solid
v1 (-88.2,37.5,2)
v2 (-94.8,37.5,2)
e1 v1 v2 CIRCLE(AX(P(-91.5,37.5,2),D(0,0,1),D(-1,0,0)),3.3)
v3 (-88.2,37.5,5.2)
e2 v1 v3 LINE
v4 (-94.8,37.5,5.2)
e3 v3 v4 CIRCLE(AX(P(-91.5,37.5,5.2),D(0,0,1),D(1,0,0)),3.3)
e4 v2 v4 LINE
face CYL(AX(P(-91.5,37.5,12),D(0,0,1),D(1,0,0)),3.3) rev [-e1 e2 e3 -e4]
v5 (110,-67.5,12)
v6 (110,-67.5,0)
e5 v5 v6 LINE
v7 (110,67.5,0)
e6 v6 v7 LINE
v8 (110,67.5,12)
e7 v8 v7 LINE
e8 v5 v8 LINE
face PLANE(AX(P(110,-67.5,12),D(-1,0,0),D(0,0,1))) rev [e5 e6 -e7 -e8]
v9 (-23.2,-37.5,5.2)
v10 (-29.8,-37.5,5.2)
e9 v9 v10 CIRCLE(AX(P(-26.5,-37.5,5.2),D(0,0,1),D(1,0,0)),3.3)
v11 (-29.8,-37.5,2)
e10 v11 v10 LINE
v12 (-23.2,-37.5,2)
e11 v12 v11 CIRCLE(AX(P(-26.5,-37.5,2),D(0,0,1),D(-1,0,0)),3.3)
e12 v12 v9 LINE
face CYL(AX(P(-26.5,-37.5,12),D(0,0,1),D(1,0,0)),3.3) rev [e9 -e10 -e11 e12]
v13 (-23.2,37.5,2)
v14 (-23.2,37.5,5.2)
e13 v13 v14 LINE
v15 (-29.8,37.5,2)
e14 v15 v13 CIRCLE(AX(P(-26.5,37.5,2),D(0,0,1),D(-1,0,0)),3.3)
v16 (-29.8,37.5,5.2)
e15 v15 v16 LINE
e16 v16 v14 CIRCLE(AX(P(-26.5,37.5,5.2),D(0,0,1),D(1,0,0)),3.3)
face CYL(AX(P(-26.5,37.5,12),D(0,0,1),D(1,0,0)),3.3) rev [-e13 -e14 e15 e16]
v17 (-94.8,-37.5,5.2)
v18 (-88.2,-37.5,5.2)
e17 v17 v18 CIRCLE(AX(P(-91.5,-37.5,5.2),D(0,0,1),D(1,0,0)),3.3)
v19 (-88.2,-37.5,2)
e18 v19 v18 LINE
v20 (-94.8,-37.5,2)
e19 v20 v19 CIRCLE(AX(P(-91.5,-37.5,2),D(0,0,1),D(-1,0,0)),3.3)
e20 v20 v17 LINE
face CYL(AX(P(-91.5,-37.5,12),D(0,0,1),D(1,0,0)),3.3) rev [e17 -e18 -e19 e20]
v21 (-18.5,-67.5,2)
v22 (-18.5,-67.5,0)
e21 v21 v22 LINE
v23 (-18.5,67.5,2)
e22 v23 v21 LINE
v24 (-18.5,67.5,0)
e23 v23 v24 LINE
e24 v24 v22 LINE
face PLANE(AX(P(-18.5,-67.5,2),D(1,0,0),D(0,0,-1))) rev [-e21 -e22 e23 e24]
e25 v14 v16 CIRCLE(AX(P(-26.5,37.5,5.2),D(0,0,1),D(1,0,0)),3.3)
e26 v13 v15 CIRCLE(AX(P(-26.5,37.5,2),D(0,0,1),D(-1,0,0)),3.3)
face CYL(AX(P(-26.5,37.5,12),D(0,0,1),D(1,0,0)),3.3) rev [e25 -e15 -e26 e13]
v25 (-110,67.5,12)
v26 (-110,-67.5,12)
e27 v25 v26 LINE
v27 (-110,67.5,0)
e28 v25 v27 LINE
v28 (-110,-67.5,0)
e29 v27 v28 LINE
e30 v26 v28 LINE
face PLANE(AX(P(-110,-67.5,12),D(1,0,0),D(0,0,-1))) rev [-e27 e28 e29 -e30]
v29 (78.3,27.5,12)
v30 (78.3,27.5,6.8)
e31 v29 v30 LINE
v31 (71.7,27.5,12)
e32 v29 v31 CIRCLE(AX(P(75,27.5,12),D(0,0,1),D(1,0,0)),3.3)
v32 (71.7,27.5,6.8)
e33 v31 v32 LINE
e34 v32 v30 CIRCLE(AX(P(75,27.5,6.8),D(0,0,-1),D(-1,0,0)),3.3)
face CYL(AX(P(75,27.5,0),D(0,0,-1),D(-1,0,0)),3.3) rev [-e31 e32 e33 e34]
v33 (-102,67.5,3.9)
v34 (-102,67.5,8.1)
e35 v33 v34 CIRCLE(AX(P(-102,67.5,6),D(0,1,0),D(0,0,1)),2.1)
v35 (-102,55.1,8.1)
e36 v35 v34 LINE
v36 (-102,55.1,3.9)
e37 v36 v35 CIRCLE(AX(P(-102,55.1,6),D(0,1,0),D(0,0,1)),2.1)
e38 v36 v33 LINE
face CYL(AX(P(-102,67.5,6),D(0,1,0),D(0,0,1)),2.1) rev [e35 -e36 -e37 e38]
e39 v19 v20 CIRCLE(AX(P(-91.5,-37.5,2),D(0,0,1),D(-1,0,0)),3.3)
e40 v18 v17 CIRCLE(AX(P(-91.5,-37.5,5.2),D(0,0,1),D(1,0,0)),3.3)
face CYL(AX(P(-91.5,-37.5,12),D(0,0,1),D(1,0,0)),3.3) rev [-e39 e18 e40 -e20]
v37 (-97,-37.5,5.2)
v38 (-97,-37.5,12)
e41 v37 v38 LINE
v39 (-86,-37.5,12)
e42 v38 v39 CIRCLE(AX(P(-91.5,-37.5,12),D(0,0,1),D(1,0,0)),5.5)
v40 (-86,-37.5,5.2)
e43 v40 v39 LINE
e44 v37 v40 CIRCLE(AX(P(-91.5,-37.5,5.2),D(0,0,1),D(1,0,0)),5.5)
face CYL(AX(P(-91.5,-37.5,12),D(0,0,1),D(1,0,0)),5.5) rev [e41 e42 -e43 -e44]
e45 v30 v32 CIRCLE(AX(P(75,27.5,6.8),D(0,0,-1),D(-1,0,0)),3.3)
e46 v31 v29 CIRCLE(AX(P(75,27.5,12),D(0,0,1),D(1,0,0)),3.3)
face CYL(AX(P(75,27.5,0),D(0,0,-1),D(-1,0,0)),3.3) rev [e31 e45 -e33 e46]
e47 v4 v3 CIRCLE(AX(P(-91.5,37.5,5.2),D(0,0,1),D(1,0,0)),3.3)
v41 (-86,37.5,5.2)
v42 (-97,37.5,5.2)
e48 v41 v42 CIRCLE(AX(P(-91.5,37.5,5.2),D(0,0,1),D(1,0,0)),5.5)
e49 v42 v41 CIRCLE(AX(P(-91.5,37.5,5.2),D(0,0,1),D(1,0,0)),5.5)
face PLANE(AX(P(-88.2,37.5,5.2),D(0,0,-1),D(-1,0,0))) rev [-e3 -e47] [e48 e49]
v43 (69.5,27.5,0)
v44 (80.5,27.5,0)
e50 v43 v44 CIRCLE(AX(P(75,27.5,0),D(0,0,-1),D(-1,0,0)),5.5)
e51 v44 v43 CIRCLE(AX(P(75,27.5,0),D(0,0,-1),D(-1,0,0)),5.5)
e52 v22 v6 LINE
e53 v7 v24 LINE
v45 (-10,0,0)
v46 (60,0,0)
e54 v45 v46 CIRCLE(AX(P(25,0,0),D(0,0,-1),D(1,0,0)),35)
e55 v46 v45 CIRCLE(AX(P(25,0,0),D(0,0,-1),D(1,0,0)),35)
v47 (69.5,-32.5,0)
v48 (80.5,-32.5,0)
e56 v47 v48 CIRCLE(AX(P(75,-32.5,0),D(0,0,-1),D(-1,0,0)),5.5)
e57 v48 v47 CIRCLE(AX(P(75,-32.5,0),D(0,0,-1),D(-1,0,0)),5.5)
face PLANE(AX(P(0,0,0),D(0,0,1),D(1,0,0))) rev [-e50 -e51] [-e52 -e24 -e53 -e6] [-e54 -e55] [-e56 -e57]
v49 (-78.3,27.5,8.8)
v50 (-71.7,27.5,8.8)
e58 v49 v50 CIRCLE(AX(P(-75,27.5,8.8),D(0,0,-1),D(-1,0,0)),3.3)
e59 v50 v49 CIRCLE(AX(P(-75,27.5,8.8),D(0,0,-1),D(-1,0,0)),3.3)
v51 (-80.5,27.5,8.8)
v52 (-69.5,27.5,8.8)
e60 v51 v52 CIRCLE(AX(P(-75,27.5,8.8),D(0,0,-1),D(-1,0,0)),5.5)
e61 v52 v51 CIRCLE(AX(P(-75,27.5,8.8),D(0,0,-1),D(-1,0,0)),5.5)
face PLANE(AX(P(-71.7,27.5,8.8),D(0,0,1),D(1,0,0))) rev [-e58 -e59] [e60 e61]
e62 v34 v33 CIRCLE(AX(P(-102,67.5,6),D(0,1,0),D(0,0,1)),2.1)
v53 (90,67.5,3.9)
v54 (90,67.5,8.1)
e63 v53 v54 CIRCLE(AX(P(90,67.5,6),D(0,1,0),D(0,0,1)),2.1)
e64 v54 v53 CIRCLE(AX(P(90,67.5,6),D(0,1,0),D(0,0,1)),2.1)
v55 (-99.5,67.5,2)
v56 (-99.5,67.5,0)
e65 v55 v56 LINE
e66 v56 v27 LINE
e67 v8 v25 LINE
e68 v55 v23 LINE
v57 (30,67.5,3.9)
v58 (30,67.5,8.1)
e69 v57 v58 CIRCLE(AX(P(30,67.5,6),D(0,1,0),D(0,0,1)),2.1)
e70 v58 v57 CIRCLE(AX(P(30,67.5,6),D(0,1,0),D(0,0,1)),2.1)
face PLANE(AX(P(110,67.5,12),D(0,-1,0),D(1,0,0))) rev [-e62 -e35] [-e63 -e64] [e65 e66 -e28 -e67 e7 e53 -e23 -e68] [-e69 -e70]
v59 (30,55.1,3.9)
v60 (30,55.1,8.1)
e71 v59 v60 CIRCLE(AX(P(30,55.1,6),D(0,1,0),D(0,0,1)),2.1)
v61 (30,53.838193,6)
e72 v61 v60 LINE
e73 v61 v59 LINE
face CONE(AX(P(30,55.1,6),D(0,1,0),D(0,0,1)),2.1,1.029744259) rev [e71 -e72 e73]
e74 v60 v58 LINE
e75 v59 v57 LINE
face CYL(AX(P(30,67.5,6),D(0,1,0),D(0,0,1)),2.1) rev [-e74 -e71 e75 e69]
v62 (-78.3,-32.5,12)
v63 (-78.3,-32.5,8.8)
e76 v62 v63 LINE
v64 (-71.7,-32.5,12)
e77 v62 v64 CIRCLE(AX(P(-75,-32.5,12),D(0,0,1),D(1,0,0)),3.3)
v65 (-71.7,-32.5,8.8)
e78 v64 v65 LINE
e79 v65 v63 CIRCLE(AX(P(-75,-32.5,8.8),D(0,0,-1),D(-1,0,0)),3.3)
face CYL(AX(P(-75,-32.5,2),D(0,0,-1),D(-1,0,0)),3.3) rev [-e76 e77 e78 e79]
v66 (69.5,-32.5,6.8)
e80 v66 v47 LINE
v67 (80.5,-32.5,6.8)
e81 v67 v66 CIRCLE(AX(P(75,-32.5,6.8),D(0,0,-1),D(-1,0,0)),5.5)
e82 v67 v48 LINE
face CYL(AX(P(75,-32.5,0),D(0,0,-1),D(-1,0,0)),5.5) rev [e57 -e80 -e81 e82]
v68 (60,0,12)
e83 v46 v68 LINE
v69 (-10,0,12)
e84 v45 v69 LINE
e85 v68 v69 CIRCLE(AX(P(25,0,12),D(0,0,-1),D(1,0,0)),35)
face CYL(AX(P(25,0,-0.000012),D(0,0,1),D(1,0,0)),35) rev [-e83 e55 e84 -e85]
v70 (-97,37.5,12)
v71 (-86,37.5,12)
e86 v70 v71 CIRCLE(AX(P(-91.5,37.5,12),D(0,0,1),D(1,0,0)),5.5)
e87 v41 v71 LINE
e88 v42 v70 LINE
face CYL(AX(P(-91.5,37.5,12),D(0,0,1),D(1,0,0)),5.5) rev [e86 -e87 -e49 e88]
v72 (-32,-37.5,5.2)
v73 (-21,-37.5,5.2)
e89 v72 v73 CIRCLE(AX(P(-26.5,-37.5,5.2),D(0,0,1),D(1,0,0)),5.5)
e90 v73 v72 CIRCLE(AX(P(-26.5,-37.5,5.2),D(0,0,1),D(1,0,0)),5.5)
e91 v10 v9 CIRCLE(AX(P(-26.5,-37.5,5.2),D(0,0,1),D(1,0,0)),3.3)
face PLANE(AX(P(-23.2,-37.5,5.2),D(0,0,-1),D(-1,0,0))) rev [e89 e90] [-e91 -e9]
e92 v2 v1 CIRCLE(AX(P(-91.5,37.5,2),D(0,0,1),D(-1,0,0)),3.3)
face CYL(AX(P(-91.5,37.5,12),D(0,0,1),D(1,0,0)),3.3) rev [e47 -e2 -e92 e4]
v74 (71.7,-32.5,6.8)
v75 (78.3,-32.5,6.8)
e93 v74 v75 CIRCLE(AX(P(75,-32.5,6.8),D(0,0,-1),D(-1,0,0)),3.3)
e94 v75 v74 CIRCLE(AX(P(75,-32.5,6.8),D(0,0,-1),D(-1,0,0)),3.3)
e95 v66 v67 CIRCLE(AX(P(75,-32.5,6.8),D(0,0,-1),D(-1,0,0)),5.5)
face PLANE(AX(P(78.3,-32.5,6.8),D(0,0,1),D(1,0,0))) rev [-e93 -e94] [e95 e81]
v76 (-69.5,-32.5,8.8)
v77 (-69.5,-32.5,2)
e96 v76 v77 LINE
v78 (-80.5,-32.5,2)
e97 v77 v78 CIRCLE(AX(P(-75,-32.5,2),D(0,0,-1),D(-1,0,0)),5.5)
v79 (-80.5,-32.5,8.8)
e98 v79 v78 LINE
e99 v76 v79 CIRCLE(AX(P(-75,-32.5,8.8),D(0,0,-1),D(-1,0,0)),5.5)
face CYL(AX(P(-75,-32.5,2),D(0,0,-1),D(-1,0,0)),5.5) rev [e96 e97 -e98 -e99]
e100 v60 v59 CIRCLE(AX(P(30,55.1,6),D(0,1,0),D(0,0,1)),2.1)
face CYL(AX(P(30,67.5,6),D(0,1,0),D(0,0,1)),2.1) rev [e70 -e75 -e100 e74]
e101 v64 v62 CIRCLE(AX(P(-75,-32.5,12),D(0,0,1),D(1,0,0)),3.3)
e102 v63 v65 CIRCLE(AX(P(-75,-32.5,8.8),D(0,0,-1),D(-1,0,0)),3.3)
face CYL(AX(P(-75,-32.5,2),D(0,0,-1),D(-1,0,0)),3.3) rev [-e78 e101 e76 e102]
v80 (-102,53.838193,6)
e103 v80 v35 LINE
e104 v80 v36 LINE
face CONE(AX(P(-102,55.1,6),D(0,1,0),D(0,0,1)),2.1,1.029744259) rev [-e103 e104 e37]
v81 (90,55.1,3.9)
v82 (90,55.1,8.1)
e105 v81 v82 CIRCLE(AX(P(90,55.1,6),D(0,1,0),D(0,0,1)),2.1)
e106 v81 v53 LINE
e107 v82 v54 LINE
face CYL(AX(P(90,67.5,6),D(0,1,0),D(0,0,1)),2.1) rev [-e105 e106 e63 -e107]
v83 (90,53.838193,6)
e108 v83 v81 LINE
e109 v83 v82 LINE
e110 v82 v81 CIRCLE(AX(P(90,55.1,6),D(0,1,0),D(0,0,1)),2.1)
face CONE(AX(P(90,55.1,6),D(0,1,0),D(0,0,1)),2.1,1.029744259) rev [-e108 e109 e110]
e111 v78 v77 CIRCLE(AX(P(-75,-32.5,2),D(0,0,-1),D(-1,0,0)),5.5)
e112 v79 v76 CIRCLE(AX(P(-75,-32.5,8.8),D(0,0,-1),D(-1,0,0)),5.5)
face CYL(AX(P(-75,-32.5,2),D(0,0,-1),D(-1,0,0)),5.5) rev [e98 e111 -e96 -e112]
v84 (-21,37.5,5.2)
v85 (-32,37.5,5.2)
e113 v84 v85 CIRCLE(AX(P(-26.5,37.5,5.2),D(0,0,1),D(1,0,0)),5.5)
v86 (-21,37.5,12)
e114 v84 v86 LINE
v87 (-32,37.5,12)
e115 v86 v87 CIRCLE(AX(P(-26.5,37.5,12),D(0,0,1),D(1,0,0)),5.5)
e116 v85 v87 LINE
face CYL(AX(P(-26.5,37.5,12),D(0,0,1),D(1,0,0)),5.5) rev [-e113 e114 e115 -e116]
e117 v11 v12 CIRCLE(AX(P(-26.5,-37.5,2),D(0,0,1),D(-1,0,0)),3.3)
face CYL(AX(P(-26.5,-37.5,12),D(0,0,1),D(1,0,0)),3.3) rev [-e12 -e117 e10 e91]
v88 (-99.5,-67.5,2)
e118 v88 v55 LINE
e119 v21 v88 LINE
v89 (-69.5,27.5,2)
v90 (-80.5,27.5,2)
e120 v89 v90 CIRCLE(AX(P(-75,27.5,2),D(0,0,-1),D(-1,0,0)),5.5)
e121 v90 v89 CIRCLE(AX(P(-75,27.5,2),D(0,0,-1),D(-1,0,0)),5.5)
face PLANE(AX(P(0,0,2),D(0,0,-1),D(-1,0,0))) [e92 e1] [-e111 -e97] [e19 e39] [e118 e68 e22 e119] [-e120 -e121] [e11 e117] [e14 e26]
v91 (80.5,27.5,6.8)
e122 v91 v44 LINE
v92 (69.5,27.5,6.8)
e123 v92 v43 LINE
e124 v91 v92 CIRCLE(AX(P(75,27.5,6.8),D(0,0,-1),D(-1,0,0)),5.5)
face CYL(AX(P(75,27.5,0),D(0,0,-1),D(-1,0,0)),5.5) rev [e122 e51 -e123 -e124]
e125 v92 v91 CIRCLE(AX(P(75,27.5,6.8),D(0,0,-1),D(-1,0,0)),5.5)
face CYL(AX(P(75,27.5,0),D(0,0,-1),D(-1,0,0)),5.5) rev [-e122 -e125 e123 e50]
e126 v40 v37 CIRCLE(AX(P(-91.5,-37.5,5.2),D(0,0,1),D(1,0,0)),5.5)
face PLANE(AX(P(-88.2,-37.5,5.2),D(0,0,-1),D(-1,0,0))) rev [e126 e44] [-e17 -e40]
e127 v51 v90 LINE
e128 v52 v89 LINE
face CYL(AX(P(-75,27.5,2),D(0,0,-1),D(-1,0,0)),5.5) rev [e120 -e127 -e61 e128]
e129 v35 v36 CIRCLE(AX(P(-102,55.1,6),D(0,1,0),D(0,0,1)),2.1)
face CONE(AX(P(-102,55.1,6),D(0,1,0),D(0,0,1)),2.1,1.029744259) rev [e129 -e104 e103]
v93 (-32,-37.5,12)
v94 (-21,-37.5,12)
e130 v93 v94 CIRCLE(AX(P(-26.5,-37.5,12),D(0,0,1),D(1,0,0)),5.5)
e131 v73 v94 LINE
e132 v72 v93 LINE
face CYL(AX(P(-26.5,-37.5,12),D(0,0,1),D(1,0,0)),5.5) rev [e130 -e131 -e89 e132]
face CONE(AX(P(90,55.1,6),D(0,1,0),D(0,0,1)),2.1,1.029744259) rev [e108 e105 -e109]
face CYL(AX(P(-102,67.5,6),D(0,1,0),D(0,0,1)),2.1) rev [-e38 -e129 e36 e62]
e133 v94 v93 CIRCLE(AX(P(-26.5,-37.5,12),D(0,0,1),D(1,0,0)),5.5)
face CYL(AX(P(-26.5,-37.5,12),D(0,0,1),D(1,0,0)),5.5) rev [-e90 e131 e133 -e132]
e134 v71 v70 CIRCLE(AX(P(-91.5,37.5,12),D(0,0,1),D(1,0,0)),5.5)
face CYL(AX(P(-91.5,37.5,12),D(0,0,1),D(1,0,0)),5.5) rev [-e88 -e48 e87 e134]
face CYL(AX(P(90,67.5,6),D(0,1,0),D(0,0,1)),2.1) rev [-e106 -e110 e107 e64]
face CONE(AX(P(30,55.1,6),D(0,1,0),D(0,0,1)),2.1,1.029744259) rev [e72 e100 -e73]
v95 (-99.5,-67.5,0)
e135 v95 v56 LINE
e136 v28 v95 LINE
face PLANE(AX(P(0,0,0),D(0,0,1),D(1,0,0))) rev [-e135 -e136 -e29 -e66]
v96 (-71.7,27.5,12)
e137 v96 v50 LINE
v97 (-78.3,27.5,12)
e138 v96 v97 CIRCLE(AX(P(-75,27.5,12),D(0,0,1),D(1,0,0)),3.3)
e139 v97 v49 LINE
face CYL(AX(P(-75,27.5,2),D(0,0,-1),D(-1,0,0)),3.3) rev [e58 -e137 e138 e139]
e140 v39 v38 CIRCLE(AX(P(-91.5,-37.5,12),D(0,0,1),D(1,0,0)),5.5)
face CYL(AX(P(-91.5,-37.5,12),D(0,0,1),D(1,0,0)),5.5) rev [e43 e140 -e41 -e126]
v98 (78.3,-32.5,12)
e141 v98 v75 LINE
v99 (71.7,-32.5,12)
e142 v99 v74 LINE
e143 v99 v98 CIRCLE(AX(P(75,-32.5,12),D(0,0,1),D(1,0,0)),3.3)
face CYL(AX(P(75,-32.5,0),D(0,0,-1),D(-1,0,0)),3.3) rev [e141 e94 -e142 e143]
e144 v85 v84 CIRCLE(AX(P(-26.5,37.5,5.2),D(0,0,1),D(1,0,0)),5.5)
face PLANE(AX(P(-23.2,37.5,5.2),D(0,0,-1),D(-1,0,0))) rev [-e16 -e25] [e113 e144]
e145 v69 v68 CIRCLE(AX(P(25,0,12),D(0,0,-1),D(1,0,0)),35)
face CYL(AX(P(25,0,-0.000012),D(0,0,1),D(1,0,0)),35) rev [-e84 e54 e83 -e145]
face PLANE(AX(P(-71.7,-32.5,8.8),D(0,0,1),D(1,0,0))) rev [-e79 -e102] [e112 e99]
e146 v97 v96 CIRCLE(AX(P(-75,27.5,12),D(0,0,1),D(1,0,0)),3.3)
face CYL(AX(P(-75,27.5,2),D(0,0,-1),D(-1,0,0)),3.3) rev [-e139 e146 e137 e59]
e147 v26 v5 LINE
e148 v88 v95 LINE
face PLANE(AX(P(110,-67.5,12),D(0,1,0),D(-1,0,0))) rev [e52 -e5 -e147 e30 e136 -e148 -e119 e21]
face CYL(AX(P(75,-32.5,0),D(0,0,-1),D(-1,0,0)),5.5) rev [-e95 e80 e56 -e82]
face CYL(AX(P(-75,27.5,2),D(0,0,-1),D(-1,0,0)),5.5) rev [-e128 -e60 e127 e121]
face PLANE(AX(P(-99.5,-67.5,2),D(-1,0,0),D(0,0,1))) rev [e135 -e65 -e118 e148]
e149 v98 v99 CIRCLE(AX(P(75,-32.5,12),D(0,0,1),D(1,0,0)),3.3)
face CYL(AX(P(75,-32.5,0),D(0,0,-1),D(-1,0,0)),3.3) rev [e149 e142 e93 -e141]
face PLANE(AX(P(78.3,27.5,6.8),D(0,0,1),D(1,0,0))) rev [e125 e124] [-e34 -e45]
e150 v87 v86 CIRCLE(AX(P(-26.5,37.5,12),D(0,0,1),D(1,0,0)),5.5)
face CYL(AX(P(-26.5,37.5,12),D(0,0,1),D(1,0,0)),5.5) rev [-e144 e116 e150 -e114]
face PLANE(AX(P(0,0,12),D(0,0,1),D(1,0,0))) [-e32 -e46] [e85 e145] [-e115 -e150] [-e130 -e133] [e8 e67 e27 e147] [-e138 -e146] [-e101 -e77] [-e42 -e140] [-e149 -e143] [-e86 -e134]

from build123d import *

# Parameters (mm, degrees)
SKETCH_1_W                      = 220
SKETCH_1_H                      = 135
EXTRUDE_1_DEPTH                 = 12
HOLE_WIZARD_1_D                 = 6.6
HOLE_WIZARD_1_CBORE_D           = 11
HOLE_WIZARD_1_CBORE_DEPTH       = 6.8
SKETCH_4_W                      = 81
SKETCH_4_H                      = 135
CUT_EXTRUDE_1_DEPTH             = 2
HOLE_WIZARD_2_D                 = 6.6
HOLE_WIZARD_2_CBORE_D           = 11
HOLE_WIZARD_2_CBORE_DEPTH       = 6.8
HOLE_WIZARD_3_D                 = 6.6
HOLE_WIZARD_3_CBORE_D           = 11
HOLE_WIZARD_3_CBORE_DEPTH       = 6.8
CUT_EXTRUDE_2_REACH             = 131.616
SKETCH_9_R                      = 35
CUT_EXTRUDE_2_DIRECTION_2_DEPTH = 130.615778361
HOLE_WIZARD_M5_1_D              = 4.2
HOLE_WIZARD_M5_1_DEPTH          = 12.4
HOLE_WIZARD_M5_1_TIP            = 1.2618073


with BuildPart() as part:
    # 草图1 → 凸台-拉伸1 (new body)
    with BuildSketch(Plane.XY):
        Rectangle(SKETCH_1_W, SKETCH_1_H)
    extrude(amount=EXTRUDE_1_DEPTH)

    # 打孔尺寸(%根据)内六角圆柱头螺钉的类型1 (through all)
    with Locations(Plane.XY.offset(12)):
        with Locations((-91.500000058, 37.5), (-26.500000058, 37.5), (-91.500000058, -37.5), (-26.500000058, -37.5)):
            CounterBoreHole(HOLE_WIZARD_1_D / 2, HOLE_WIZARD_1_CBORE_D / 2, HOLE_WIZARD_1_CBORE_DEPTH)

    # 草图4 → 切除-拉伸1 (cut)
    with BuildSketch(Plane(origin=(0, 0, 0), x_dir=(-1, 0, 0), z_dir=(0, 0, -1))):
        with Locations((59.000000058, 0)):
            Rectangle(SKETCH_4_W, SKETCH_4_H)
    extrude(amount=-CUT_EXTRUDE_1_DEPTH, mode=Mode.SUBTRACT)

    # 打孔尺寸(%根据)内六角圆柱头螺钉的类型2 (through all)
    with Locations(Plane(origin=(0, 0, 2), x_dir=(-1, 0, 0), z_dir=(0, 0, -1))):
        with Locations((75, -32.5), (75, 27.5)):
            CounterBoreHole(HOLE_WIZARD_2_D / 2, HOLE_WIZARD_2_CBORE_D / 2, HOLE_WIZARD_2_CBORE_DEPTH)

    # 打孔尺寸(%根据)内六角圆柱头螺钉的类型3 (through all)
    with Locations(Plane(origin=(0, 0, 0), x_dir=(-1, 0, 0), z_dir=(0, 0, -1))):
        with Locations((-75, -32.5), (-75, 27.5)):
            CounterBoreHole(HOLE_WIZARD_3_D / 2, HOLE_WIZARD_3_CBORE_D / 2, HOLE_WIZARD_3_CBORE_DEPTH)

    # 草图9 → 切除-拉伸2 (cut, up to next)
    with BuildSketch(Plane(origin=(0, 0, 0), x_dir=(-1, 0, 0), z_dir=(0, 0, -1)), mode=Mode.PRIVATE) as cut_extrude_2_sk1:
        with Locations(Location((-25, 0, 0), (0, 0, 180))):
            Circle(SKETCH_9_R)
    cut_extrude_2_tool1 = extrude(cut_extrude_2_sk1.sketch, amount=-CUT_EXTRUDE_2_REACH, mode=Mode.PRIVATE) & part.part
    add(cut_extrude_2_tool1.solids().sort_by_distance((25, 0, 0))[0], mode=Mode.SUBTRACT)

    # 草图9 → 切除-拉伸2 direction 2 (cut)
    with BuildSketch(Plane(origin=(0, 0, 0), x_dir=(-1, 0, 0), z_dir=(0, 0, -1))):
        with Locations(Location((-25, 0, 0), (0, 0, 180))):
            Circle(SKETCH_9_R)
    extrude(amount=CUT_EXTRUDE_2_DIRECTION_2_DEPTH, mode=Mode.SUBTRACT)

    # M5 螺纹孔1
    with Locations(Plane(origin=(0, 67.5, 0), x_dir=(1, 0, 0), z_dir=(0, 1, 0))):
        with Locations((90, -6), (30, -6), (-102, -6)):
            Hole(HOLE_WIZARD_M5_1_D / 2, depth=HOLE_WIZARD_M5_1_DEPTH)
            with Locations((0, 0, -(HOLE_WIZARD_M5_1_DEPTH + HOLE_WIZARD_M5_1_TIP / 2))):  # 118° drill point
                Cone(0, HOLE_WIZARD_M5_1_D / 2, HOLE_WIZARD_M5_1_TIP, mode=Mode.SUBTRACT)


solid = part.part
